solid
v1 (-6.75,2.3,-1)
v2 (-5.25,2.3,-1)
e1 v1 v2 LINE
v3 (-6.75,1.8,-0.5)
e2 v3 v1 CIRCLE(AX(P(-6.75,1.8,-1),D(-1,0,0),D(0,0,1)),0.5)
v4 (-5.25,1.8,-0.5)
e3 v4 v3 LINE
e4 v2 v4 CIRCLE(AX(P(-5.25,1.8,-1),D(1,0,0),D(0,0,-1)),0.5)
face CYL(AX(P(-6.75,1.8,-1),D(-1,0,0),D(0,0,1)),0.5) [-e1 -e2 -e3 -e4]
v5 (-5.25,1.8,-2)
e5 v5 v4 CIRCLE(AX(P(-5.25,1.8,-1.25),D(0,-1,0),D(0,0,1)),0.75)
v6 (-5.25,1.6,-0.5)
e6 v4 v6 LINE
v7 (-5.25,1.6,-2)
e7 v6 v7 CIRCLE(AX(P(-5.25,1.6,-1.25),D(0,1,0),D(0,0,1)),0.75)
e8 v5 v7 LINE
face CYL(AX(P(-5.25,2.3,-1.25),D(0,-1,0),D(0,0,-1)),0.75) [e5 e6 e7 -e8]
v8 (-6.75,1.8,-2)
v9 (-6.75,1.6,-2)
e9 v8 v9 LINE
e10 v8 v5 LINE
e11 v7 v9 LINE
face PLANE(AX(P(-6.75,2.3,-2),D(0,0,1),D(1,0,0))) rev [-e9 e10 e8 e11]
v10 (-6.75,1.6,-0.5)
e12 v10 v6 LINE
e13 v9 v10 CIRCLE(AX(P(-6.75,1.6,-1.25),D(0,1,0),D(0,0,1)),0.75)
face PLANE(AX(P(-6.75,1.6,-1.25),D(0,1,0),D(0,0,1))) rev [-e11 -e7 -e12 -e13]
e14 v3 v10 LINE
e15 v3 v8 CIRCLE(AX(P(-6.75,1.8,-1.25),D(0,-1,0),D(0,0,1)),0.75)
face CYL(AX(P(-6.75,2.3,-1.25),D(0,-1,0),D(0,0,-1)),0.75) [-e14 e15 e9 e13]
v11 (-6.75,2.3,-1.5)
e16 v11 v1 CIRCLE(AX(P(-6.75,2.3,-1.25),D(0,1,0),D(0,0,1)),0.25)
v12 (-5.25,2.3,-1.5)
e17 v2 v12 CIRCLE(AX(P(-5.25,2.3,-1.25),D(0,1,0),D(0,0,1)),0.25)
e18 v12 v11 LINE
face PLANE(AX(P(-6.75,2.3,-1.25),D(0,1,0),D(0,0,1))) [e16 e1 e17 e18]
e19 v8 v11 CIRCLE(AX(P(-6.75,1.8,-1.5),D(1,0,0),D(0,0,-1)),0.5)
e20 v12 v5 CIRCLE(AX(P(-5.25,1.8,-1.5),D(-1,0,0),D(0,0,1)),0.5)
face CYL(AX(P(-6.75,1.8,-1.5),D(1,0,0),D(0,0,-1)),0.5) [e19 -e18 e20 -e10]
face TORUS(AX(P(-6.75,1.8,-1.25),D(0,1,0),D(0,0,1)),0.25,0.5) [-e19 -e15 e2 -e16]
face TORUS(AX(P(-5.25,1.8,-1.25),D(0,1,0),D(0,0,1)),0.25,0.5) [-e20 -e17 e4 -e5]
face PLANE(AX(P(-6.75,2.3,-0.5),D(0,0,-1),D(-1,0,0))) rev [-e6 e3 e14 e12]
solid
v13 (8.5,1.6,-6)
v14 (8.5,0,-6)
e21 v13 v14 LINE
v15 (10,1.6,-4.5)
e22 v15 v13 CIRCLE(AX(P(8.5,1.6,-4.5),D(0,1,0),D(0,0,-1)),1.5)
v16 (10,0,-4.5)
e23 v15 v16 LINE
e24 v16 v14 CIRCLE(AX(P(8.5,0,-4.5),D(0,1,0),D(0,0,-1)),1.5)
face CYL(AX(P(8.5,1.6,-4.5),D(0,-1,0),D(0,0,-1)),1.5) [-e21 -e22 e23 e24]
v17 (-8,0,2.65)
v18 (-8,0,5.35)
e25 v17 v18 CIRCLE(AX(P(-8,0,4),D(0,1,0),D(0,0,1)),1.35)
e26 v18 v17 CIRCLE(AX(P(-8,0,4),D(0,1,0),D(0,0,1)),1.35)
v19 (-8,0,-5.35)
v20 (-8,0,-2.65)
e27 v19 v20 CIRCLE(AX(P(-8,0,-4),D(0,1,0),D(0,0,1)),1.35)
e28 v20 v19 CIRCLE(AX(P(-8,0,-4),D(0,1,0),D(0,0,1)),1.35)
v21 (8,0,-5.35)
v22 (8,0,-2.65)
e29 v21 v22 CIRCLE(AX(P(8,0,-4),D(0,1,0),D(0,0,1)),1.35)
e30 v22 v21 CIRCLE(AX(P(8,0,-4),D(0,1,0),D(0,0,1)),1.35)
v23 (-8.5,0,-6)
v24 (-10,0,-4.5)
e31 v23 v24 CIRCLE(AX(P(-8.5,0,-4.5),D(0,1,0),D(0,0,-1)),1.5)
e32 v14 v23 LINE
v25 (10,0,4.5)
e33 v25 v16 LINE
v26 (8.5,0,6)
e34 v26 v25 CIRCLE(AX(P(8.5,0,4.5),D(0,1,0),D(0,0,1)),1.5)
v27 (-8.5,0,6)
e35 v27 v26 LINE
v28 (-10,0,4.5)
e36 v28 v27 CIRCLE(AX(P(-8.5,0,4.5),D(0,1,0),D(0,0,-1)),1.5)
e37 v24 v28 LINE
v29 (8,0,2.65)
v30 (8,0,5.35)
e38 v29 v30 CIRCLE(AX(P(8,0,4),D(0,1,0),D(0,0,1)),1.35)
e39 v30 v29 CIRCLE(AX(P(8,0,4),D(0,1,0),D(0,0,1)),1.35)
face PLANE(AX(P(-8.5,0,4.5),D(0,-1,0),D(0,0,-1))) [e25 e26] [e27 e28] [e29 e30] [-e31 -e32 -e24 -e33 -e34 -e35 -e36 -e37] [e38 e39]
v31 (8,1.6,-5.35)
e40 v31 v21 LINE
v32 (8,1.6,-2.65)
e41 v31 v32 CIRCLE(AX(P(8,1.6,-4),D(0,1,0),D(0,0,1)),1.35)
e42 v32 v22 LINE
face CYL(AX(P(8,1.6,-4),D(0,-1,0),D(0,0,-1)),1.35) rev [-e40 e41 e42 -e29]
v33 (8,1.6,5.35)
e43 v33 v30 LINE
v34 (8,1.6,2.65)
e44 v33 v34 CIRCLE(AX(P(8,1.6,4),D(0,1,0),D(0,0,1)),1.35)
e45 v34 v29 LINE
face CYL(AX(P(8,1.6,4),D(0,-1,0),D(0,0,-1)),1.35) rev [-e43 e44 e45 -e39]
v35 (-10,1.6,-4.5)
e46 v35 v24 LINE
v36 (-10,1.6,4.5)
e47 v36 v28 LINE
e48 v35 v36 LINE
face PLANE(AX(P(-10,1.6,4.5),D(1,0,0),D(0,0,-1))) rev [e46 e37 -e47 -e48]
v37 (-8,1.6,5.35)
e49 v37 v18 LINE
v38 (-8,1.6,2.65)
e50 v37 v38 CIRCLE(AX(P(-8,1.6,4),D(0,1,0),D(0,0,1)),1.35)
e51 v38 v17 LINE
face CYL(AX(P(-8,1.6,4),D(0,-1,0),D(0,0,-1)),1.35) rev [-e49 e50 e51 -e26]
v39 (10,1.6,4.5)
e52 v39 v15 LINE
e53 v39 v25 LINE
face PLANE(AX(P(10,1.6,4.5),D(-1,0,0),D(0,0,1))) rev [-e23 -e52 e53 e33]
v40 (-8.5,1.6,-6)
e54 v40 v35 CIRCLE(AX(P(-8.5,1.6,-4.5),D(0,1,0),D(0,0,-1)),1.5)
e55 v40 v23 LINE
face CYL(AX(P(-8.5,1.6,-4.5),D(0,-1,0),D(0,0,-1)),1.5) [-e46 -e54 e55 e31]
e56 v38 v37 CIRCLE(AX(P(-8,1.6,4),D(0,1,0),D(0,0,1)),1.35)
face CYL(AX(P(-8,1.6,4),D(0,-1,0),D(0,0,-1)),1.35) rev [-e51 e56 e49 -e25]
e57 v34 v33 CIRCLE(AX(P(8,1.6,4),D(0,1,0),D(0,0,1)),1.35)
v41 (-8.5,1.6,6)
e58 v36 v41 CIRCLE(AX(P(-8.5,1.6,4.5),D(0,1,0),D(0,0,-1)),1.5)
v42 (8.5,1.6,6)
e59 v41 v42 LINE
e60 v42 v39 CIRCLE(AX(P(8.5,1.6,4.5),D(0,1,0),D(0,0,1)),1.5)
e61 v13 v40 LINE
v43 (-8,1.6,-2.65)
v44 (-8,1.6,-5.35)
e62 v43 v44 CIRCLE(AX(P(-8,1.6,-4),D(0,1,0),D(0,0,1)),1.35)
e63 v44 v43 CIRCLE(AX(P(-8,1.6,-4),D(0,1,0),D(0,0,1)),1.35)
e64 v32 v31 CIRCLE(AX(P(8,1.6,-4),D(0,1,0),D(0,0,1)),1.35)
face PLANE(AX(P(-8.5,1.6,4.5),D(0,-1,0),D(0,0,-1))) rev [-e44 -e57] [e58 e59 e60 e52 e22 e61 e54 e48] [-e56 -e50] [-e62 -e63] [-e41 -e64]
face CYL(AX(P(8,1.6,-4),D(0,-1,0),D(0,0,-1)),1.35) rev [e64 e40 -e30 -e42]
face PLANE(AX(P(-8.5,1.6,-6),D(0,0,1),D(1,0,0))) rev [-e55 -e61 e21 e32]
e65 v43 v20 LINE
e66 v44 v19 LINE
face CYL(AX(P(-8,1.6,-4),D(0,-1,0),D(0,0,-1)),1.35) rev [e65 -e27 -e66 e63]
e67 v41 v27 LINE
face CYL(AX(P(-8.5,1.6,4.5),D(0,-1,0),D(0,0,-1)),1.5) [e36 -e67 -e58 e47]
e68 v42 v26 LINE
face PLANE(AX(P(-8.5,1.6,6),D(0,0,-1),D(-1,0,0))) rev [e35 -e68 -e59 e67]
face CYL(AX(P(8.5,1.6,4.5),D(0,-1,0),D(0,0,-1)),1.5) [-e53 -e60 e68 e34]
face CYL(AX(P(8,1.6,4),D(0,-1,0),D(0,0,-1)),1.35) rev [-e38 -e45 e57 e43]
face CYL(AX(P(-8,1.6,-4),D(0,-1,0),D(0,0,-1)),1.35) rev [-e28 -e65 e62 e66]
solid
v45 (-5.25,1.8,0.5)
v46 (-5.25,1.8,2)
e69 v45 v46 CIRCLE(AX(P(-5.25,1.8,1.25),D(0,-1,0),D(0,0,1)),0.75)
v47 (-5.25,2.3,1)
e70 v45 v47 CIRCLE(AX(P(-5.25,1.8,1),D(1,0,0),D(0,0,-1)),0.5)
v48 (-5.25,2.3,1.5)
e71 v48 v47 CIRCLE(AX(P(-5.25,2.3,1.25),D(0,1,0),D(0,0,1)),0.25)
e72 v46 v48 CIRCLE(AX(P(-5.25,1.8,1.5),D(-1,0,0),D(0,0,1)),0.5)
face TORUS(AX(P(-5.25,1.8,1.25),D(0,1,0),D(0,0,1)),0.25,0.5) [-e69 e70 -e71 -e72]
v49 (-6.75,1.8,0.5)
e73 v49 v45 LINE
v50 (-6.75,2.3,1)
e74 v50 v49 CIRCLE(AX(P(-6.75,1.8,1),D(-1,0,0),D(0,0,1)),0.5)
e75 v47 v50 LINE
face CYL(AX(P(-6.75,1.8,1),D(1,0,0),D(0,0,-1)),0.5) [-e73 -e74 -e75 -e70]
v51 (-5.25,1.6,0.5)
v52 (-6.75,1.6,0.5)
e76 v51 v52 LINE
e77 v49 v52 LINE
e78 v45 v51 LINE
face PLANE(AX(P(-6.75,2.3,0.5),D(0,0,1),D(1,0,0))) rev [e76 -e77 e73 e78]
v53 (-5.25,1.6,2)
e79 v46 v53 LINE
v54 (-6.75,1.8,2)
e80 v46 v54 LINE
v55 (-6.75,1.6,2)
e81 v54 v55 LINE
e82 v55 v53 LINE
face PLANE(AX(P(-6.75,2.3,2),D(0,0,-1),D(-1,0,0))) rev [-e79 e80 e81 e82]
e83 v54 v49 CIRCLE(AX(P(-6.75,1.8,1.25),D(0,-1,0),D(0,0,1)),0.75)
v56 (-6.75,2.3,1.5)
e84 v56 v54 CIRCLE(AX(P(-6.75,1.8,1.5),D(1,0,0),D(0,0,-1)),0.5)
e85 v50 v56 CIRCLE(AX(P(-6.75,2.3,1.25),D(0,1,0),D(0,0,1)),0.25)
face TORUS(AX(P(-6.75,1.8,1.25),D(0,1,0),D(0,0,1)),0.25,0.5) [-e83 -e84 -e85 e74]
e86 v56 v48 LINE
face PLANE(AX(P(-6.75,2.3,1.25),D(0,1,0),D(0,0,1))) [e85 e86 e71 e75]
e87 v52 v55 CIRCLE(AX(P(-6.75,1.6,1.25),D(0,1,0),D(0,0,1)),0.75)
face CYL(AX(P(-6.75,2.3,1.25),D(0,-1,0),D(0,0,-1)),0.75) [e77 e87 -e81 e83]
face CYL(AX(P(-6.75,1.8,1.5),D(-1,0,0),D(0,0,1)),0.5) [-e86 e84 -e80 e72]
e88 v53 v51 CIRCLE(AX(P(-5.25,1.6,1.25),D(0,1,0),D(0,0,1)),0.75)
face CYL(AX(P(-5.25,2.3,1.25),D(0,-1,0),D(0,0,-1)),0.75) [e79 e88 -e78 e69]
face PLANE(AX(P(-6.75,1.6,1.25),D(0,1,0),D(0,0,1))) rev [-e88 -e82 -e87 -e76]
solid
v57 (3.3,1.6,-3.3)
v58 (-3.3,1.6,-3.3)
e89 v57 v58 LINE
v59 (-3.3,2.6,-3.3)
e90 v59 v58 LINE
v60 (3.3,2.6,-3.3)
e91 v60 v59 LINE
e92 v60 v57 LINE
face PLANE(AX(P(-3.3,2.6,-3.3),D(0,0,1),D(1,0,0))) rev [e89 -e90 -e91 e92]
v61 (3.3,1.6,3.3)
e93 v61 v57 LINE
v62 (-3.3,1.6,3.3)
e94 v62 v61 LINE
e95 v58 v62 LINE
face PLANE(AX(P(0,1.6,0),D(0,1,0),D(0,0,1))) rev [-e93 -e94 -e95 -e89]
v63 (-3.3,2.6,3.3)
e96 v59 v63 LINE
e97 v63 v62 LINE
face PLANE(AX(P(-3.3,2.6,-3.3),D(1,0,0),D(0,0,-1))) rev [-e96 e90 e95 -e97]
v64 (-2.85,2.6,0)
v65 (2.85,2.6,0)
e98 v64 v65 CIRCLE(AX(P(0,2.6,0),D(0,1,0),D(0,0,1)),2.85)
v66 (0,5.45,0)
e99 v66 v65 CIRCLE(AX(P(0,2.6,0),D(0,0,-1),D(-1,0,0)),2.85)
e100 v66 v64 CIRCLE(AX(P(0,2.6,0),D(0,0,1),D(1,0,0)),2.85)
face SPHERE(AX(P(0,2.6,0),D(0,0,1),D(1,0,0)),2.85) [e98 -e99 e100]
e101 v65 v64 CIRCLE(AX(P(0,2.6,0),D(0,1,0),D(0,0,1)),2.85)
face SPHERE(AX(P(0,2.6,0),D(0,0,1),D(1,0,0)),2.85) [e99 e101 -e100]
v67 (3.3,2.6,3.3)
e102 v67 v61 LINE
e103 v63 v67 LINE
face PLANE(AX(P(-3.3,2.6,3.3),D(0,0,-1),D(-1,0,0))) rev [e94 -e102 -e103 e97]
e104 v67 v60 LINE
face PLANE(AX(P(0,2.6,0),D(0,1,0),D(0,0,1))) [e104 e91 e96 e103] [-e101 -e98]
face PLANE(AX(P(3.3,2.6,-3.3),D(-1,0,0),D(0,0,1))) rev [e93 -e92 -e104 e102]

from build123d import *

# Parameters (mm, degrees)
EXTRUDE_375_DEPTH     = 1.6
SKETCH_7_R            = 1.35
CUT_EXTRUDE_535_DEPTH = 12.771151176
SKETCH_574_W          = 6.6
SKETCH_574_H          = 6.6
EXTRUDE_767_DEPTH     = 1
EXTRUDE_1228_DEPTH    = 0.7
EXTRUDE_1228_2_DEPTH  = 0.7
FILLET_1_R            = 0.5
FILLET_2_R            = 0.5


with BuildPart() as part:
    # Sketch 232 → Extrude 375 (new body)
    with BuildSketch(Plane(origin=(0, 0, 0), x_dir=(1, 0, 0), z_dir=(0, 1, 0))):
        with BuildLine():
            Line((-8.5, -6), (8.5, -6))
            ThreePointArc((8.5, -6), (9.560660172, -5.560660172), (10, -4.5))
            Line((10, -4.5), (10, 4.5))
            ThreePointArc((10, 4.5), (9.560660172, 5.560660172), (8.5, 6))
            Line((8.5, 6), (-8.5, 6))
            ThreePointArc((-8.5, 6), (-9.560660172, 5.560660172), (-10, 4.5))
            Line((-10, 4.5), (-10, -4.5))
            ThreePointArc((-10, -4.5), (-9.560660172, -5.560660172), (-8.5, -6))
        make_face()
    extrude(amount=EXTRUDE_375_DEPTH)

    # 草图7 → Cut-Extrude 535 (cut, through all)
    with BuildSketch(Plane(origin=(0, 0, 0), x_dir=(1, 0, 0), z_dir=(0, 1, 0))):
        with Locations(Location((-8, -4, 0), (0, 0, 270))):
            Circle(SKETCH_7_R)
        with Locations(Location((8, -4, 0), (0, 0, 270))):
            Circle(SKETCH_7_R)
        with Locations(Location((8, 4, 0), (0, 0, 270))):
            Circle(SKETCH_7_R)
        with Locations(Location((-8, 4, 0), (0, 0, 270))):
            Circle(SKETCH_7_R)
    extrude(amount=CUT_EXTRUDE_535_DEPTH, mode=Mode.SUBTRACT)


with BuildPart() as body_2:
    # Sketch 574 → Extrude 767 (new body)
    with BuildSketch(Plane(origin=(0, 1.6, 0), x_dir=(1, 0, 0), z_dir=(0, 1, 0))):
        Rectangle(SKETCH_574_W, SKETCH_574_H)
    extrude(amount=EXTRUDE_767_DEPTH)

    # Sketch 806 → Revolve 870 (revolve)
    with BuildSketch(Plane.XY):
        with BuildLine():
            Line((0, 2.6), (2.85, 2.6))
            ThreePointArc((2.85, 2.6), (2.015254326, 4.615254326), (0, 5.45))
            Line((0, 5.45), (0, 2.6))
        make_face()
    revolve(axis=Axis((0, 2.6, 0), (0, 1, 0)))


with BuildPart() as body_3:
    # Sketch 926 → Extrude 1228 (new body)
    with BuildSketch(Plane(origin=(0, 1.6, 0), x_dir=(1, 0, 0), z_dir=(0, 1, 0))):
        with BuildLine():
            Line((-6.75, 2), (-5.25, 2))
            ThreePointArc((-5.25, 2), (-4.5, 1.25), (-5.25, 0.5))
            Line((-5.25, 0.5), (-6.75, 0.5))
            ThreePointArc((-6.75, 0.5), (-7.5, 1.25), (-6.75, 2))
        make_face()
    extrude(amount=EXTRUDE_1228_DEPTH)

    # 焊点1
    fillet_1_edges = [body_3.edges().sort_by_distance(p)[0] for p in [
        (-4.5, 2.3, -1.25),
        (-6, 2.3, -2),
        (-7.5, 2.3, -1.25),
        (-6, 2.3, -0.5),
    ]]
    fillet(fillet_1_edges, radius=FILLET_1_R)


with BuildPart() as body_4:
    # Sketch 926 → Extrude 1228 2 (new body)
    with BuildSketch(Plane(origin=(0, 1.6, 0), x_dir=(1, 0, 0), z_dir=(0, 1, 0))):
        with BuildLine():
            Line((-6.75, -0.5), (-5.25, -0.5))
            ThreePointArc((-5.25, -0.5), (-4.5, -1.25), (-5.25, -2))
            Line((-5.25, -2), (-6.75, -2))
            ThreePointArc((-6.75, -2), (-7.5, -1.25), (-6.75, -0.5))
        make_face()
    extrude(amount=EXTRUDE_1228_2_DEPTH)

    # 焊点2
    fillet_2_edges = [body_4.edges().sort_by_distance(p)[0] for p in [
        (-7.5, 2.3, 1.25),
        (-6, 2.3, 2),
        (-4.5, 2.3, 1.25),
        (-6, 2.3, 0.5),
    ]]
    fillet(fillet_2_edges, radius=FILLET_2_R)


solid = Compound([part.part, body_2.part, body_3.part, body_4.part])
